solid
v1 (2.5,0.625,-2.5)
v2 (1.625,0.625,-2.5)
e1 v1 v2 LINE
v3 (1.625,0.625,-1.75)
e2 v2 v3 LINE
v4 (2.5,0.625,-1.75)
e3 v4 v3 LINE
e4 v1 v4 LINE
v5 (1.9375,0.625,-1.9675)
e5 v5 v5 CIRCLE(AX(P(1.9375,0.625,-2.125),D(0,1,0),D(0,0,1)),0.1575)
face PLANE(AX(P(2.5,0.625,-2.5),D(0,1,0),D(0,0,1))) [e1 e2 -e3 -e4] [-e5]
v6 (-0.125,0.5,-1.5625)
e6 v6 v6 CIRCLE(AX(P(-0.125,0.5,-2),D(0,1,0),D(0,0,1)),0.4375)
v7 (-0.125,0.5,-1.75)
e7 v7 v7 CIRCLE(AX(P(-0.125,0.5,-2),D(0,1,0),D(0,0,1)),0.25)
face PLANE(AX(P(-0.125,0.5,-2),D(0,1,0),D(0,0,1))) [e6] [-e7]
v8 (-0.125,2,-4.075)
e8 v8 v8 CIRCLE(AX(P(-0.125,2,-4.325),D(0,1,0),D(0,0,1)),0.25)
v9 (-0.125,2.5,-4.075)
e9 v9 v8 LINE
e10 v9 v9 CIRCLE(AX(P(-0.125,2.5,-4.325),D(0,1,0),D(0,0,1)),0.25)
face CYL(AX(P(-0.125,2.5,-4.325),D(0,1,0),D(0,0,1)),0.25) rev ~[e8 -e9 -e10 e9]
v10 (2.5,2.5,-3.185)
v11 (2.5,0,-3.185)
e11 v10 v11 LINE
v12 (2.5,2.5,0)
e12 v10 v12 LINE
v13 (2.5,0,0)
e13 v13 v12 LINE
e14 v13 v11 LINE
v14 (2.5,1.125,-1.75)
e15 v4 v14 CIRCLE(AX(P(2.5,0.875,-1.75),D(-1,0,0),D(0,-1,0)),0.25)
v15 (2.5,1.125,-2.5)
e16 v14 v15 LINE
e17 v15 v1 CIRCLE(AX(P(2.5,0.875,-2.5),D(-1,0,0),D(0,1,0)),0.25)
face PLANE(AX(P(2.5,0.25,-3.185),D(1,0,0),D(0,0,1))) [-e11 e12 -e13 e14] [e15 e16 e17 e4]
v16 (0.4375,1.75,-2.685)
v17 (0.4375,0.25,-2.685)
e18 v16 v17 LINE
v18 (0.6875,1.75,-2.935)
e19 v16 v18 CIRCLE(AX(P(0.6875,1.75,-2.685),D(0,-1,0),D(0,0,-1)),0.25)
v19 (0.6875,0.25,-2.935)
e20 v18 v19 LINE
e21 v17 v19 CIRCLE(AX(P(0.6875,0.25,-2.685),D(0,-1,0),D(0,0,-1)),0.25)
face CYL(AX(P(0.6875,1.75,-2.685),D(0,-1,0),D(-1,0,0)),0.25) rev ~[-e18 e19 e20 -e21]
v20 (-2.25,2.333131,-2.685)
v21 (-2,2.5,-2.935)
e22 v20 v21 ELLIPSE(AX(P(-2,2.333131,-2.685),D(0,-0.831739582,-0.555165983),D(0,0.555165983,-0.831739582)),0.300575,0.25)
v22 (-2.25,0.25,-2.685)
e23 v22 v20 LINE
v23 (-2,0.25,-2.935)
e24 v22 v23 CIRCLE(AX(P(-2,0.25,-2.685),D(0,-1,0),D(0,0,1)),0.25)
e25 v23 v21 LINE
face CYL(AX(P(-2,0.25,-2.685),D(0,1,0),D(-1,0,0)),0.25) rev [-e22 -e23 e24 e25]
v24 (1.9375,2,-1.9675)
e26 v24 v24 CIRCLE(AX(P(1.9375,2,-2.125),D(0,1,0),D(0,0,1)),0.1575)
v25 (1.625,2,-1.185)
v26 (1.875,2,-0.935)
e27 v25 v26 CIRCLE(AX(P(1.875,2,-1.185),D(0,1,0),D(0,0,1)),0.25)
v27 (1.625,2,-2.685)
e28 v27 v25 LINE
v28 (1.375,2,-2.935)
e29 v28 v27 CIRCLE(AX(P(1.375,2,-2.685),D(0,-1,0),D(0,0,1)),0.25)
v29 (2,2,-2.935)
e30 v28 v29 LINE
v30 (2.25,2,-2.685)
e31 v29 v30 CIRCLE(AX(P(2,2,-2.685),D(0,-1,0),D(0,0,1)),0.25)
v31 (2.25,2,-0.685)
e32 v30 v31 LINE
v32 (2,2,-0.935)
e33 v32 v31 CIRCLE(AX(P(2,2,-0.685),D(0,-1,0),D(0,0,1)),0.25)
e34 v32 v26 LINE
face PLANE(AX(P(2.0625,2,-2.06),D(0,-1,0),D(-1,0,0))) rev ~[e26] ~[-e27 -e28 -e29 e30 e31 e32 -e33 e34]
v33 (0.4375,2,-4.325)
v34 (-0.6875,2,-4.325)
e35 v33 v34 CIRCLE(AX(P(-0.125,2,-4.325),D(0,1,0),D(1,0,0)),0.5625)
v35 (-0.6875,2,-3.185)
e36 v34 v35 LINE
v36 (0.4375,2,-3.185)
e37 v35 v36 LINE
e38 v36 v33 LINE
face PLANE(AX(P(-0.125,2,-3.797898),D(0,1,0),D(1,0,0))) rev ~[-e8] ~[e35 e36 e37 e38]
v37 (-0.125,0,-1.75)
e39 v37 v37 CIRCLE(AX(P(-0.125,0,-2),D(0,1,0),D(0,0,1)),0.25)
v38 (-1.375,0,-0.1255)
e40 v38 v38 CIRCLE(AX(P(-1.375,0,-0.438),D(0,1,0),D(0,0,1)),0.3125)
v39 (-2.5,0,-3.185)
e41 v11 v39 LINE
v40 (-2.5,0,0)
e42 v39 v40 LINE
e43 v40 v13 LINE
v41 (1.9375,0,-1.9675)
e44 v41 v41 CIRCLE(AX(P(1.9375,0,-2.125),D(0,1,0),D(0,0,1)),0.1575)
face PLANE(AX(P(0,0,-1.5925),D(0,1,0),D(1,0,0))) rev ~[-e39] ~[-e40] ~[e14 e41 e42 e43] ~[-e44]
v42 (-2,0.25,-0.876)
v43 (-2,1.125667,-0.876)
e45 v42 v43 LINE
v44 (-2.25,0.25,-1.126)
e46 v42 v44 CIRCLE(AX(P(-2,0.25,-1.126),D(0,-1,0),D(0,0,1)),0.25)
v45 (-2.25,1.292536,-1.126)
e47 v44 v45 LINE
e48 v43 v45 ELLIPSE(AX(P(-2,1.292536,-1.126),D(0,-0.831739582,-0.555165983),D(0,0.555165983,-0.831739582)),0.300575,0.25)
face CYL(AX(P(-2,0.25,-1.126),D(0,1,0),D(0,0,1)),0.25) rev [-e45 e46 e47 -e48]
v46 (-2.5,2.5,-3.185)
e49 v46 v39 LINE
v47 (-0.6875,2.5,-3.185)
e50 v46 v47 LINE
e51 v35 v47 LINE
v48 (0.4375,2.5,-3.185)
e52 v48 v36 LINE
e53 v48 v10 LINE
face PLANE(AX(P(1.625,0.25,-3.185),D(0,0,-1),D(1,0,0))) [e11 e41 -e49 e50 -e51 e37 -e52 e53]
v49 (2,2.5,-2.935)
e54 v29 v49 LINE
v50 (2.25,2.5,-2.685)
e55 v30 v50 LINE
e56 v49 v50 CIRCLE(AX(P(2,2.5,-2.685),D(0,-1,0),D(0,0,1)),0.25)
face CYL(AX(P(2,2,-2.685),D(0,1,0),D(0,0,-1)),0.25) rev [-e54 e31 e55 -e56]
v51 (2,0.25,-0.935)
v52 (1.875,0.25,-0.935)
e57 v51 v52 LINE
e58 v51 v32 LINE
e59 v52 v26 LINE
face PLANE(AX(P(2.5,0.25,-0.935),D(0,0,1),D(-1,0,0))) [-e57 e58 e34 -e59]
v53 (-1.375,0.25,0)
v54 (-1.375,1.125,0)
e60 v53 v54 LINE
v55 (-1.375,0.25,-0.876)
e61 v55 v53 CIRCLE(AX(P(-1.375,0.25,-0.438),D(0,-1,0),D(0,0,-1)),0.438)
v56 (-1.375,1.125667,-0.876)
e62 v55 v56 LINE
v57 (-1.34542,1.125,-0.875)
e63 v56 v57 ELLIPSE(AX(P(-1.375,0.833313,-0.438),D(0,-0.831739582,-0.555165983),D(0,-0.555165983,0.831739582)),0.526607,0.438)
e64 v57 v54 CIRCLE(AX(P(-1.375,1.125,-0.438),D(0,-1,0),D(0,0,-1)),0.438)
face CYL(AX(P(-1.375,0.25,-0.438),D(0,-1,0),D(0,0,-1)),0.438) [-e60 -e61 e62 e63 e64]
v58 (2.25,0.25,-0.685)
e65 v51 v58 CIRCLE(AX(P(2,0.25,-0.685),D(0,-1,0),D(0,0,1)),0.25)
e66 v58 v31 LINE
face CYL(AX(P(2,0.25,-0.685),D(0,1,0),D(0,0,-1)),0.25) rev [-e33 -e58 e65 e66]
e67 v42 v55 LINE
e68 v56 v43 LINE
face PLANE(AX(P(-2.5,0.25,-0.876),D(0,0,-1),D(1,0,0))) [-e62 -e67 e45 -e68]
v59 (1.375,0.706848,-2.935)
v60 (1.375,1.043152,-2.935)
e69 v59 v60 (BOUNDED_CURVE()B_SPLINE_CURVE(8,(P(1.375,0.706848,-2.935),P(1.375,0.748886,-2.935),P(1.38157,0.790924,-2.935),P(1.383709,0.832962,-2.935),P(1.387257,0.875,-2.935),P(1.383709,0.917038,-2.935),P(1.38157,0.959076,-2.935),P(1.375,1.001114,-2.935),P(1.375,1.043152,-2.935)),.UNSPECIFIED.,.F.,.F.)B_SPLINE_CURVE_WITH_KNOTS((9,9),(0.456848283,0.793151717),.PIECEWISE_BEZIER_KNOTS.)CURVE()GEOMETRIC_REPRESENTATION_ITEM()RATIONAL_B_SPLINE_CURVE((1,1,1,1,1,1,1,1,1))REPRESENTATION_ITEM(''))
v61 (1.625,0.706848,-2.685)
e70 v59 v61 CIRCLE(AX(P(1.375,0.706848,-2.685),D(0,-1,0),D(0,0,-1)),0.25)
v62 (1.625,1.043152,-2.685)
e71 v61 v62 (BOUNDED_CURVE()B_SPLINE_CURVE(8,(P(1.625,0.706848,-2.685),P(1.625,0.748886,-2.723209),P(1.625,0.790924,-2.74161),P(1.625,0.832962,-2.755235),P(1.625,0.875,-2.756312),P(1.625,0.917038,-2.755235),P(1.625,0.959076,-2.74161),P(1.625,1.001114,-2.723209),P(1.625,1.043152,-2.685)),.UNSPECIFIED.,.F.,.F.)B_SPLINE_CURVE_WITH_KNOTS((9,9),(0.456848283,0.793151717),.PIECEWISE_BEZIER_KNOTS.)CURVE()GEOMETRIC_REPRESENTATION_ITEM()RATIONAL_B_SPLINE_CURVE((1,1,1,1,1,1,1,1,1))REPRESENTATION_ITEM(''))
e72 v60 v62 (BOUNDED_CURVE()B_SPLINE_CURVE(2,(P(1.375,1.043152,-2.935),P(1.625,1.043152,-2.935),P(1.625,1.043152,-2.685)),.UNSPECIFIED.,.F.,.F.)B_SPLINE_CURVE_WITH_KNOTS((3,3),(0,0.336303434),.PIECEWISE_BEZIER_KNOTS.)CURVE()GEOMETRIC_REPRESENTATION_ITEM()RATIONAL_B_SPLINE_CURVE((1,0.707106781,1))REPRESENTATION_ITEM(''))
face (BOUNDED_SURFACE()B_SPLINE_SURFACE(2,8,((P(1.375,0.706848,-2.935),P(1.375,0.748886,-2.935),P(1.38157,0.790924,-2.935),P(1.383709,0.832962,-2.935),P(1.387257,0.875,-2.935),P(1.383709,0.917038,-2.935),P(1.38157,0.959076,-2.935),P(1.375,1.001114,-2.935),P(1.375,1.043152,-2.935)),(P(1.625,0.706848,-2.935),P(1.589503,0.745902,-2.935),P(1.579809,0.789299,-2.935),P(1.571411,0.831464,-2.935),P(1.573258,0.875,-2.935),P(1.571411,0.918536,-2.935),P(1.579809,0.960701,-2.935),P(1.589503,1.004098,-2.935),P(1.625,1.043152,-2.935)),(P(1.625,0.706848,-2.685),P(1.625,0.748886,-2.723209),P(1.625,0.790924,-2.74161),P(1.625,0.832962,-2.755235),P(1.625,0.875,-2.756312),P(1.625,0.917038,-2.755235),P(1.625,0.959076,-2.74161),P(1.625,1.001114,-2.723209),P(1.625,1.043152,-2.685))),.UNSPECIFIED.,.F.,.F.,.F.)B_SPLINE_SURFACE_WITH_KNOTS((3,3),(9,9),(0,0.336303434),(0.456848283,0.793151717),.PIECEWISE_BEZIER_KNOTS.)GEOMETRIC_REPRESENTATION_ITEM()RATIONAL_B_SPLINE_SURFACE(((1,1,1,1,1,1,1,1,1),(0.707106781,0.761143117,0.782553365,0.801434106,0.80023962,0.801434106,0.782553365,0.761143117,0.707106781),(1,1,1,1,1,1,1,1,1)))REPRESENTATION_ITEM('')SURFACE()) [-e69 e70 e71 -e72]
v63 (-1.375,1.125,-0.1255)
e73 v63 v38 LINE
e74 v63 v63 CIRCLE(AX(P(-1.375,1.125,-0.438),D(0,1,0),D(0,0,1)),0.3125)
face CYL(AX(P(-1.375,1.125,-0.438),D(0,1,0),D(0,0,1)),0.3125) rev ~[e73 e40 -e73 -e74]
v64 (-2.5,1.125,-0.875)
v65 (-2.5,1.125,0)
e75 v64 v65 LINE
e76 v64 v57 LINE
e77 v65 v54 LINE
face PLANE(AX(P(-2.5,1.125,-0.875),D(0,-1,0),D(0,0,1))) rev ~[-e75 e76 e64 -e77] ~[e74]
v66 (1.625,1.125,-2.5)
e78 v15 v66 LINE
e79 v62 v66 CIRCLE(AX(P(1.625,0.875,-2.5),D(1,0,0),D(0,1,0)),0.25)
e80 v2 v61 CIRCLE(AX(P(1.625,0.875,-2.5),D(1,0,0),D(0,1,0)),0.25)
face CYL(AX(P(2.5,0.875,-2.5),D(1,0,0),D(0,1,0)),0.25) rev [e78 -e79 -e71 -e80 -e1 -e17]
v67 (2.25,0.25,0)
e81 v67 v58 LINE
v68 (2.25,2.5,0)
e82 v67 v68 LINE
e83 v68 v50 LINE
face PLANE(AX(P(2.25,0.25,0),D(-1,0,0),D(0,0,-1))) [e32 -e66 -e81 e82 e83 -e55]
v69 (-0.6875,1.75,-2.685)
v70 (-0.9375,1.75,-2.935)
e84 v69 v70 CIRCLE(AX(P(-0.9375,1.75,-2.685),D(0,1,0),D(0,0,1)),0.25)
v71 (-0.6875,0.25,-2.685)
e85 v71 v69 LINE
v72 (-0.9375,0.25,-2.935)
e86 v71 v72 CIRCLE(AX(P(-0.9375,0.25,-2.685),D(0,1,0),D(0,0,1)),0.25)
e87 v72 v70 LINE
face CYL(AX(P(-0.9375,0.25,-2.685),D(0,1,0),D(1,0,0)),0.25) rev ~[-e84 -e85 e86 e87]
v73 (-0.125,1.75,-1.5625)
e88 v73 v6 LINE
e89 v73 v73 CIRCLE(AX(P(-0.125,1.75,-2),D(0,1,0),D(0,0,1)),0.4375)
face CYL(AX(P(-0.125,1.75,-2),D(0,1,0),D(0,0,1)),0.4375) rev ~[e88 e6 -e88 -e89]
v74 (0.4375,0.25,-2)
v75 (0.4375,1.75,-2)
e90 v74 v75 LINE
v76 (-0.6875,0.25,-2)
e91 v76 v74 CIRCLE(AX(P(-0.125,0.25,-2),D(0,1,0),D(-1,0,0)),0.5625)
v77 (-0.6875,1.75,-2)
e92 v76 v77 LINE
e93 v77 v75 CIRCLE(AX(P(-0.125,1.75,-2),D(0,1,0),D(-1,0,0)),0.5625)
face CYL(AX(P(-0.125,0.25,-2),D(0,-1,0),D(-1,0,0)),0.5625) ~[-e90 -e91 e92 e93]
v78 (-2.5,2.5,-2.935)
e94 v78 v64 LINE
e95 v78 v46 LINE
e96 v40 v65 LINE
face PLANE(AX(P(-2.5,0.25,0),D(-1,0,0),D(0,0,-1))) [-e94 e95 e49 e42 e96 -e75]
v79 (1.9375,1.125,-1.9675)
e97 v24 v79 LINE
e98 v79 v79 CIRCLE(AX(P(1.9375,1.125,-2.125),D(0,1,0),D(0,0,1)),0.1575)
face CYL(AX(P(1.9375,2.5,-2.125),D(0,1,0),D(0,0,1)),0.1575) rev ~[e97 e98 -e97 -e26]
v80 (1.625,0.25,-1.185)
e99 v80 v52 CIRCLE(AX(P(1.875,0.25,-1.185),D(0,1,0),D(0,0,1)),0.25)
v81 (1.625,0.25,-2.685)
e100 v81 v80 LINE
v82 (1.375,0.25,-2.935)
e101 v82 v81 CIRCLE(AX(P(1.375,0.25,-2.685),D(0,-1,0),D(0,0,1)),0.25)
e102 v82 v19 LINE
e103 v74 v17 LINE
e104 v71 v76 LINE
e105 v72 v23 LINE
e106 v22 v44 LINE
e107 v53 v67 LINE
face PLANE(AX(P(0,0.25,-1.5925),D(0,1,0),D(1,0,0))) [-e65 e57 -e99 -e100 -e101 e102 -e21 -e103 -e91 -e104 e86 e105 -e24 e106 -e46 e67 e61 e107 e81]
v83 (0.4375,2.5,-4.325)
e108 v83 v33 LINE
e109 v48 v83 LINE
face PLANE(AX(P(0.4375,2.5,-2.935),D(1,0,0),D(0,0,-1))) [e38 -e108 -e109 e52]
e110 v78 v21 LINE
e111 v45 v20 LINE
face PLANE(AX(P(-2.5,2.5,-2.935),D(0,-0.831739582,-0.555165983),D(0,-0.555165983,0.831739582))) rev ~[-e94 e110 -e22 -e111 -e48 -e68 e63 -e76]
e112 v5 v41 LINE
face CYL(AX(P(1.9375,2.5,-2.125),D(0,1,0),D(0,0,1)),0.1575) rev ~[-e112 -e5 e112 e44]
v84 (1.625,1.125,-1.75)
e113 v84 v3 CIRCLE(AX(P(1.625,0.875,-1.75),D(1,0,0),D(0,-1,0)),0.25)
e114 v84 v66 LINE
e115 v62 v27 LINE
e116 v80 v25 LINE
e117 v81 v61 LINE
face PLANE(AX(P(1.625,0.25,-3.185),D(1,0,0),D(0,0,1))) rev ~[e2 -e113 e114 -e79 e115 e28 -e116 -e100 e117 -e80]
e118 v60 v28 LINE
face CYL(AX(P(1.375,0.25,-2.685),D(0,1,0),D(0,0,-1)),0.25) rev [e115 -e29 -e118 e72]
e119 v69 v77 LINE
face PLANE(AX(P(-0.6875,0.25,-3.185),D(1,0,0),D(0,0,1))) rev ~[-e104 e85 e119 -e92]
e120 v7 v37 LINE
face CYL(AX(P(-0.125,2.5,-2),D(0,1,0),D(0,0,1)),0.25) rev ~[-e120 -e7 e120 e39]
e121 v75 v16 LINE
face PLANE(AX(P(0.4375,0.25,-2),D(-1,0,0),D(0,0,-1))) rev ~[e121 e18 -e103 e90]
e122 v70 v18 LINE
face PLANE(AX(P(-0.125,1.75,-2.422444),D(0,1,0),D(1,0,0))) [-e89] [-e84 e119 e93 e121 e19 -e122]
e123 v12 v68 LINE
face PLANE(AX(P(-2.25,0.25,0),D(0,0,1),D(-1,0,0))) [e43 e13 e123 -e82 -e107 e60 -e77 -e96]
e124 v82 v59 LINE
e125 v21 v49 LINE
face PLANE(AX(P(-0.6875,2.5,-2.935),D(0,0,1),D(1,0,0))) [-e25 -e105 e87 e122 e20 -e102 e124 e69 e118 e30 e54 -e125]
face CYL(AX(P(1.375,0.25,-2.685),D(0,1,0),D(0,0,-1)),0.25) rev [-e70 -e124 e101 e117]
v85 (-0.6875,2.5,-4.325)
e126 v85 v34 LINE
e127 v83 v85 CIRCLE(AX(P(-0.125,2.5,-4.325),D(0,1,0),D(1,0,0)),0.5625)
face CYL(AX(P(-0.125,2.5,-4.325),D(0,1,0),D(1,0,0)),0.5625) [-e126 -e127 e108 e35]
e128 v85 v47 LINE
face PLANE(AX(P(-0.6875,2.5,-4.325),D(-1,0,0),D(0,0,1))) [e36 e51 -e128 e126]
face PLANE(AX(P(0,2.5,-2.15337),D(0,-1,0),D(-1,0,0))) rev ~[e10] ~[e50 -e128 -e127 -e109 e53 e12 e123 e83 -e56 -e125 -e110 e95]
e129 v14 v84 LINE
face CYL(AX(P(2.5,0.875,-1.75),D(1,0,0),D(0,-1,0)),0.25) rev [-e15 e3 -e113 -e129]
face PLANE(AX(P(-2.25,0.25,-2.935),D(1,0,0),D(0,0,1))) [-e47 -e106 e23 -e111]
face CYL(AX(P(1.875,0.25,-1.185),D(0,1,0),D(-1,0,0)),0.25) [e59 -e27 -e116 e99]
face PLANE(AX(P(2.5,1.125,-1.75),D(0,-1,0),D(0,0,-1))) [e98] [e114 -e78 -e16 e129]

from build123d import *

# Parameters (mm, degrees)
BASE_PLATE_DEPTH              = 0.25
PERIMETER_WALLS_DEPTH         = 2.25
CORNER_BOSS_DEPTH             = 1.125
WALL_POCKET_CUT_DEPTH         = 2.125
CENTRAL_BOSS_DEPTH            = 1.5
MOUNTING_TAB_DEPTH            = 1.75
SIDE_WALL_SLOT_DEPTH          = 1.75
WALL_LIP_DEPTH                = 0.5
PROFILE_TRIM_SKETCH_R         = 0.25
PROFILE_TRIM_SKETCH_R_2       = 0.1575
PROFILE_TRIM_SKETCH_R_3       = 0.2205
PROFILE_TRIM_CUT_DEPTH        = 3.5
TAB_EDGE_FILLET_R0_25_R       = 0.25
TAB_WALL_FILLET_1_R0_25_R     = 0.25
TAB_WALL_FILLET_2_R0_25_R     = 0.25
CENTRAL_BOSS_FILLET_1_R0_25_R = 0.25
CENTRAL_BOSS_FILLET_2_R0_25_R = 0.25
WALL_FILLET_1_R0_25_R         = 0.25
CORNER_BOSS_FILLET_R0_25_R    = 0.25
WALL_FILLET_2_R0_25_R         = 0.25
BOSS_HOLE_SKETCH_0_875_R      = 0.4375
BOSS_HOLE_0_875_DEPTH         = 1.25
HOLE_SKETCH_0_625_R           = 0.3125
HOLE_0_625_DEPTH              = 1.25


with BuildPart() as part:
    # Base Plate Sketch → Base Plate (new body)
    with BuildSketch(Plane(origin=(0, 0, 0), x_dir=(1, 0, 0), z_dir=(0, 1, 0))):
        Polygon((0, 0), (2.5, 0), (2.5, 3.185), (-2.5, 3.185), (-2.5, 0), align=None)
    extrude(amount=BASE_PLATE_DEPTH)

    # Perimeter Walls Sketch → Perimeter Walls (add)
    with BuildSketch(Plane(origin=(0, 0.25, 0), x_dir=(1, 0, 0), z_dir=(0, 1, 0))):
        Polygon((-2.5, 0), (-2.5, 3.185), (2.5, 3.185), (2.5, 0), (2.25, 0), (2.25, 2.935), (-2.25, 2.935), (-2.25, 0), align=None)
    extrude(amount=PERIMETER_WALLS_DEPTH)

    # Corner Boss Sketch → Corner Boss (add)
    with BuildSketch(Plane(origin=(0, 0.25, 0), x_dir=(1, 0, 0), z_dir=(0, 1, 0))):
        with BuildLine():
            Line((-2.5, 0), (-2.5, 0.438))
            Line((-2.5, 0.438), (-2.5, 0.876))
            Line((-2.5, 0.876), (-1.375, 0.876))
            ThreePointArc((-1.375, 0.876), (-0.937, 0.438), (-1.375, 0))
            Line((-1.375, 0), (-2.5, 0))
        make_face()
    extrude(amount=CORNER_BOSS_DEPTH)

    # Wall Pocket Sketch → Wall Pocket Cut (cut)
    with BuildSketch(Plane.ZY.offset(2.5)):
        Polygon((0, 2.5), (-2.935, 2.5), (-0.875, 1.125), (0, 1.125), align=None)
    extrude(amount=-WALL_POCKET_CUT_DEPTH, mode=Mode.SUBTRACT)

    # Central Boss Sketch → Central Boss (add)
    with BuildSketch(Plane(origin=(0, 0.25, 0), x_dir=(1, 0, 0), z_dir=(0, 1, 0))):
        with BuildLine():
            ThreePointArc((-0.6875, 2), (-0.125, 1.4375), (0.4375, 2))
            Line((0.4375, 2), (0.4375, 2.935))
            Line((0.4375, 2.935), (0.4375, 3.185))
            Line((0.4375, 3.185), (-0.6875, 3.185))
            Line((-0.6875, 3.185), (-0.6875, 2))
        make_face()
    extrude(amount=CENTRAL_BOSS_DEPTH)

    # Mounting Tab Sketch → Mounting Tab (add)
    with BuildSketch(Plane(origin=(0, 0.25, 0), x_dir=(1, 0, 0), z_dir=(0, 1, 0))):
        Polygon((2.5, 3.185), (2.5, 0.935), (1.625, 0.935), (1.625, 2.935), (1.625, 3.185), align=None)
    extrude(amount=MOUNTING_TAB_DEPTH)

    # Side Slot Sketch → Side Wall Slot (cut)
    with BuildSketch(Plane(origin=(2.5, 0, 0), x_dir=(0, 0, -1), z_dir=(1, 0, 0))):
        with BuildLine():
            Line((1.75, 1.125), (2.5, 1.125))
            ThreePointArc((2.5, 1.125), (2.75, 0.875), (2.5, 0.625))
            Line((2.5, 0.625), (1.75, 0.625))
            ThreePointArc((1.75, 0.625), (1.5, 0.875), (1.75, 1.125))
        make_face()
    extrude(amount=-SIDE_WALL_SLOT_DEPTH, mode=Mode.SUBTRACT)

    # Wall Lip Sketch → Wall Lip (add)
    with BuildSketch(Plane(origin=(0, 2.5, 0), x_dir=(1, 0, 0), z_dir=(0, 1, 0))):
        with BuildLine():
            Line((-0.6875, 2.935), (0.4375, 2.935))
            Line((0.4375, 2.935), (0.4375, 4.325))
            ThreePointArc((0.4375, 4.325), (-0.125, 4.8875), (-0.6875, 4.325))
            Line((-0.6875, 4.325), (-0.6875, 2.935))
        make_face()
    extrude(amount=-WALL_LIP_DEPTH)

    # Profile Trim Sketch → Profile Trim Cut (cut)
    with BuildSketch(Plane(origin=(0, 2.5, 0), x_dir=(1, 0, 0), z_dir=(0, 1, 0))):
        with Locations(Location((-0.125, 4.325, 0), (0, 0, 270))):
            Circle(PROFILE_TRIM_SKETCH_R)
        with Locations(Location((1.9375, 2.125, 0), (0, 0, 270))):
            Circle(PROFILE_TRIM_SKETCH_R_2)
        with Locations(Location((-1.375, 0.438, 0), (0, 0, 270))):
            Circle(PROFILE_TRIM_SKETCH_R_3)
        with Locations(Location((-0.125, 2, 0), (0, 0, 270))):
            Circle(PROFILE_TRIM_SKETCH_R)
    extrude(amount=-PROFILE_TRIM_CUT_DEPTH, mode=Mode.SUBTRACT)

    # Tab Edge Fillet R0.25
    tab_edge_fillet_r0_25_edges = [part.edges().sort_by_distance(p)[0] for p in [
        (1.625, 1.125, -0.935),
    ]]
    fillet(tab_edge_fillet_r0_25_edges, radius=TAB_EDGE_FILLET_R0_25_R)

    # Tab-Wall Fillet 1 R0.25
    tab_wall_fillet_1_r0_25_edges = [part.edges().sort_by_distance(p)[0] for p in [
        (2.25, 1.125, -0.935),
    ]]
    fillet(tab_wall_fillet_1_r0_25_edges, radius=TAB_WALL_FILLET_1_R0_25_R)

    # Tab-Wall Fillet 2 R0.25
    tab_wall_fillet_2_r0_25_edges = [part.edges().sort_by_distance(p)[0] for p in [
        (1.625, 1.125, -2.935),
    ]]
    fillet(tab_wall_fillet_2_r0_25_edges, radius=TAB_WALL_FILLET_2_R0_25_R)

    # Central Boss Fillet 1 R0.25
    central_boss_fillet_1_r0_25_edges = [part.edges().sort_by_distance(p)[0] for p in [
        (0.4375, 1, -2.935),
    ]]
    fillet(central_boss_fillet_1_r0_25_edges, radius=CENTRAL_BOSS_FILLET_1_R0_25_R)

    # Central Boss Fillet 2 R0.25
    central_boss_fillet_2_r0_25_edges = [part.edges().sort_by_distance(p)[0] for p in [
        (-0.6875, 1, -2.935),
    ]]
    fillet(central_boss_fillet_2_r0_25_edges, radius=CENTRAL_BOSS_FILLET_2_R0_25_R)

    # Wall Fillet 1 R0.25
    wall_fillet_1_r0_25_edges = [part.edges().sort_by_distance(p)[0] for p in [
        (-2.25, 1.375, -2.935),
    ]]
    fillet(wall_fillet_1_r0_25_edges, radius=WALL_FILLET_1_R0_25_R)

    # Corner Boss Fillet R0.25
    corner_boss_fillet_r0_25_edges = [part.edges().sort_by_distance(p)[0] for p in [
        (-2.25, 0.687833738, -0.876),
    ]]
    fillet(corner_boss_fillet_r0_25_edges, radius=CORNER_BOSS_FILLET_R0_25_R)

    # Wall Fillet 2 R0.25
    wall_fillet_2_r0_25_edges = [part.edges().sort_by_distance(p)[0] for p in [
        (2.25, 2.25, -2.935),
    ]]
    fillet(wall_fillet_2_r0_25_edges, radius=WALL_FILLET_2_R0_25_R)

    # Boss Hole Sketch Ø0.875 → Boss Hole Ø0.875 (cut)
    with BuildSketch(Plane(origin=(0, 1.75, 0), x_dir=(1, 0, 0), z_dir=(0, 1, 0))):
        with Locations(Location((-0.125, 2, 0), (0, 0, 270))):
            Circle(BOSS_HOLE_SKETCH_0_875_R)
    extrude(amount=-BOSS_HOLE_0_875_DEPTH, mode=Mode.SUBTRACT)

    # Hole Sketch Ø0.625 → Hole Ø0.625 (cut)
    with BuildSketch(Plane(origin=(0, 1.125, 0), x_dir=(1, 0, 0), z_dir=(0, 1, 0))):
        with Locations(Location((-1.375, 0.438, 0), (0, 0, 270))):
            Circle(HOLE_SKETCH_0_625_R)
    extrude(amount=-HOLE_0_625_DEPTH, mode=Mode.SUBTRACT)


solid = part.part
